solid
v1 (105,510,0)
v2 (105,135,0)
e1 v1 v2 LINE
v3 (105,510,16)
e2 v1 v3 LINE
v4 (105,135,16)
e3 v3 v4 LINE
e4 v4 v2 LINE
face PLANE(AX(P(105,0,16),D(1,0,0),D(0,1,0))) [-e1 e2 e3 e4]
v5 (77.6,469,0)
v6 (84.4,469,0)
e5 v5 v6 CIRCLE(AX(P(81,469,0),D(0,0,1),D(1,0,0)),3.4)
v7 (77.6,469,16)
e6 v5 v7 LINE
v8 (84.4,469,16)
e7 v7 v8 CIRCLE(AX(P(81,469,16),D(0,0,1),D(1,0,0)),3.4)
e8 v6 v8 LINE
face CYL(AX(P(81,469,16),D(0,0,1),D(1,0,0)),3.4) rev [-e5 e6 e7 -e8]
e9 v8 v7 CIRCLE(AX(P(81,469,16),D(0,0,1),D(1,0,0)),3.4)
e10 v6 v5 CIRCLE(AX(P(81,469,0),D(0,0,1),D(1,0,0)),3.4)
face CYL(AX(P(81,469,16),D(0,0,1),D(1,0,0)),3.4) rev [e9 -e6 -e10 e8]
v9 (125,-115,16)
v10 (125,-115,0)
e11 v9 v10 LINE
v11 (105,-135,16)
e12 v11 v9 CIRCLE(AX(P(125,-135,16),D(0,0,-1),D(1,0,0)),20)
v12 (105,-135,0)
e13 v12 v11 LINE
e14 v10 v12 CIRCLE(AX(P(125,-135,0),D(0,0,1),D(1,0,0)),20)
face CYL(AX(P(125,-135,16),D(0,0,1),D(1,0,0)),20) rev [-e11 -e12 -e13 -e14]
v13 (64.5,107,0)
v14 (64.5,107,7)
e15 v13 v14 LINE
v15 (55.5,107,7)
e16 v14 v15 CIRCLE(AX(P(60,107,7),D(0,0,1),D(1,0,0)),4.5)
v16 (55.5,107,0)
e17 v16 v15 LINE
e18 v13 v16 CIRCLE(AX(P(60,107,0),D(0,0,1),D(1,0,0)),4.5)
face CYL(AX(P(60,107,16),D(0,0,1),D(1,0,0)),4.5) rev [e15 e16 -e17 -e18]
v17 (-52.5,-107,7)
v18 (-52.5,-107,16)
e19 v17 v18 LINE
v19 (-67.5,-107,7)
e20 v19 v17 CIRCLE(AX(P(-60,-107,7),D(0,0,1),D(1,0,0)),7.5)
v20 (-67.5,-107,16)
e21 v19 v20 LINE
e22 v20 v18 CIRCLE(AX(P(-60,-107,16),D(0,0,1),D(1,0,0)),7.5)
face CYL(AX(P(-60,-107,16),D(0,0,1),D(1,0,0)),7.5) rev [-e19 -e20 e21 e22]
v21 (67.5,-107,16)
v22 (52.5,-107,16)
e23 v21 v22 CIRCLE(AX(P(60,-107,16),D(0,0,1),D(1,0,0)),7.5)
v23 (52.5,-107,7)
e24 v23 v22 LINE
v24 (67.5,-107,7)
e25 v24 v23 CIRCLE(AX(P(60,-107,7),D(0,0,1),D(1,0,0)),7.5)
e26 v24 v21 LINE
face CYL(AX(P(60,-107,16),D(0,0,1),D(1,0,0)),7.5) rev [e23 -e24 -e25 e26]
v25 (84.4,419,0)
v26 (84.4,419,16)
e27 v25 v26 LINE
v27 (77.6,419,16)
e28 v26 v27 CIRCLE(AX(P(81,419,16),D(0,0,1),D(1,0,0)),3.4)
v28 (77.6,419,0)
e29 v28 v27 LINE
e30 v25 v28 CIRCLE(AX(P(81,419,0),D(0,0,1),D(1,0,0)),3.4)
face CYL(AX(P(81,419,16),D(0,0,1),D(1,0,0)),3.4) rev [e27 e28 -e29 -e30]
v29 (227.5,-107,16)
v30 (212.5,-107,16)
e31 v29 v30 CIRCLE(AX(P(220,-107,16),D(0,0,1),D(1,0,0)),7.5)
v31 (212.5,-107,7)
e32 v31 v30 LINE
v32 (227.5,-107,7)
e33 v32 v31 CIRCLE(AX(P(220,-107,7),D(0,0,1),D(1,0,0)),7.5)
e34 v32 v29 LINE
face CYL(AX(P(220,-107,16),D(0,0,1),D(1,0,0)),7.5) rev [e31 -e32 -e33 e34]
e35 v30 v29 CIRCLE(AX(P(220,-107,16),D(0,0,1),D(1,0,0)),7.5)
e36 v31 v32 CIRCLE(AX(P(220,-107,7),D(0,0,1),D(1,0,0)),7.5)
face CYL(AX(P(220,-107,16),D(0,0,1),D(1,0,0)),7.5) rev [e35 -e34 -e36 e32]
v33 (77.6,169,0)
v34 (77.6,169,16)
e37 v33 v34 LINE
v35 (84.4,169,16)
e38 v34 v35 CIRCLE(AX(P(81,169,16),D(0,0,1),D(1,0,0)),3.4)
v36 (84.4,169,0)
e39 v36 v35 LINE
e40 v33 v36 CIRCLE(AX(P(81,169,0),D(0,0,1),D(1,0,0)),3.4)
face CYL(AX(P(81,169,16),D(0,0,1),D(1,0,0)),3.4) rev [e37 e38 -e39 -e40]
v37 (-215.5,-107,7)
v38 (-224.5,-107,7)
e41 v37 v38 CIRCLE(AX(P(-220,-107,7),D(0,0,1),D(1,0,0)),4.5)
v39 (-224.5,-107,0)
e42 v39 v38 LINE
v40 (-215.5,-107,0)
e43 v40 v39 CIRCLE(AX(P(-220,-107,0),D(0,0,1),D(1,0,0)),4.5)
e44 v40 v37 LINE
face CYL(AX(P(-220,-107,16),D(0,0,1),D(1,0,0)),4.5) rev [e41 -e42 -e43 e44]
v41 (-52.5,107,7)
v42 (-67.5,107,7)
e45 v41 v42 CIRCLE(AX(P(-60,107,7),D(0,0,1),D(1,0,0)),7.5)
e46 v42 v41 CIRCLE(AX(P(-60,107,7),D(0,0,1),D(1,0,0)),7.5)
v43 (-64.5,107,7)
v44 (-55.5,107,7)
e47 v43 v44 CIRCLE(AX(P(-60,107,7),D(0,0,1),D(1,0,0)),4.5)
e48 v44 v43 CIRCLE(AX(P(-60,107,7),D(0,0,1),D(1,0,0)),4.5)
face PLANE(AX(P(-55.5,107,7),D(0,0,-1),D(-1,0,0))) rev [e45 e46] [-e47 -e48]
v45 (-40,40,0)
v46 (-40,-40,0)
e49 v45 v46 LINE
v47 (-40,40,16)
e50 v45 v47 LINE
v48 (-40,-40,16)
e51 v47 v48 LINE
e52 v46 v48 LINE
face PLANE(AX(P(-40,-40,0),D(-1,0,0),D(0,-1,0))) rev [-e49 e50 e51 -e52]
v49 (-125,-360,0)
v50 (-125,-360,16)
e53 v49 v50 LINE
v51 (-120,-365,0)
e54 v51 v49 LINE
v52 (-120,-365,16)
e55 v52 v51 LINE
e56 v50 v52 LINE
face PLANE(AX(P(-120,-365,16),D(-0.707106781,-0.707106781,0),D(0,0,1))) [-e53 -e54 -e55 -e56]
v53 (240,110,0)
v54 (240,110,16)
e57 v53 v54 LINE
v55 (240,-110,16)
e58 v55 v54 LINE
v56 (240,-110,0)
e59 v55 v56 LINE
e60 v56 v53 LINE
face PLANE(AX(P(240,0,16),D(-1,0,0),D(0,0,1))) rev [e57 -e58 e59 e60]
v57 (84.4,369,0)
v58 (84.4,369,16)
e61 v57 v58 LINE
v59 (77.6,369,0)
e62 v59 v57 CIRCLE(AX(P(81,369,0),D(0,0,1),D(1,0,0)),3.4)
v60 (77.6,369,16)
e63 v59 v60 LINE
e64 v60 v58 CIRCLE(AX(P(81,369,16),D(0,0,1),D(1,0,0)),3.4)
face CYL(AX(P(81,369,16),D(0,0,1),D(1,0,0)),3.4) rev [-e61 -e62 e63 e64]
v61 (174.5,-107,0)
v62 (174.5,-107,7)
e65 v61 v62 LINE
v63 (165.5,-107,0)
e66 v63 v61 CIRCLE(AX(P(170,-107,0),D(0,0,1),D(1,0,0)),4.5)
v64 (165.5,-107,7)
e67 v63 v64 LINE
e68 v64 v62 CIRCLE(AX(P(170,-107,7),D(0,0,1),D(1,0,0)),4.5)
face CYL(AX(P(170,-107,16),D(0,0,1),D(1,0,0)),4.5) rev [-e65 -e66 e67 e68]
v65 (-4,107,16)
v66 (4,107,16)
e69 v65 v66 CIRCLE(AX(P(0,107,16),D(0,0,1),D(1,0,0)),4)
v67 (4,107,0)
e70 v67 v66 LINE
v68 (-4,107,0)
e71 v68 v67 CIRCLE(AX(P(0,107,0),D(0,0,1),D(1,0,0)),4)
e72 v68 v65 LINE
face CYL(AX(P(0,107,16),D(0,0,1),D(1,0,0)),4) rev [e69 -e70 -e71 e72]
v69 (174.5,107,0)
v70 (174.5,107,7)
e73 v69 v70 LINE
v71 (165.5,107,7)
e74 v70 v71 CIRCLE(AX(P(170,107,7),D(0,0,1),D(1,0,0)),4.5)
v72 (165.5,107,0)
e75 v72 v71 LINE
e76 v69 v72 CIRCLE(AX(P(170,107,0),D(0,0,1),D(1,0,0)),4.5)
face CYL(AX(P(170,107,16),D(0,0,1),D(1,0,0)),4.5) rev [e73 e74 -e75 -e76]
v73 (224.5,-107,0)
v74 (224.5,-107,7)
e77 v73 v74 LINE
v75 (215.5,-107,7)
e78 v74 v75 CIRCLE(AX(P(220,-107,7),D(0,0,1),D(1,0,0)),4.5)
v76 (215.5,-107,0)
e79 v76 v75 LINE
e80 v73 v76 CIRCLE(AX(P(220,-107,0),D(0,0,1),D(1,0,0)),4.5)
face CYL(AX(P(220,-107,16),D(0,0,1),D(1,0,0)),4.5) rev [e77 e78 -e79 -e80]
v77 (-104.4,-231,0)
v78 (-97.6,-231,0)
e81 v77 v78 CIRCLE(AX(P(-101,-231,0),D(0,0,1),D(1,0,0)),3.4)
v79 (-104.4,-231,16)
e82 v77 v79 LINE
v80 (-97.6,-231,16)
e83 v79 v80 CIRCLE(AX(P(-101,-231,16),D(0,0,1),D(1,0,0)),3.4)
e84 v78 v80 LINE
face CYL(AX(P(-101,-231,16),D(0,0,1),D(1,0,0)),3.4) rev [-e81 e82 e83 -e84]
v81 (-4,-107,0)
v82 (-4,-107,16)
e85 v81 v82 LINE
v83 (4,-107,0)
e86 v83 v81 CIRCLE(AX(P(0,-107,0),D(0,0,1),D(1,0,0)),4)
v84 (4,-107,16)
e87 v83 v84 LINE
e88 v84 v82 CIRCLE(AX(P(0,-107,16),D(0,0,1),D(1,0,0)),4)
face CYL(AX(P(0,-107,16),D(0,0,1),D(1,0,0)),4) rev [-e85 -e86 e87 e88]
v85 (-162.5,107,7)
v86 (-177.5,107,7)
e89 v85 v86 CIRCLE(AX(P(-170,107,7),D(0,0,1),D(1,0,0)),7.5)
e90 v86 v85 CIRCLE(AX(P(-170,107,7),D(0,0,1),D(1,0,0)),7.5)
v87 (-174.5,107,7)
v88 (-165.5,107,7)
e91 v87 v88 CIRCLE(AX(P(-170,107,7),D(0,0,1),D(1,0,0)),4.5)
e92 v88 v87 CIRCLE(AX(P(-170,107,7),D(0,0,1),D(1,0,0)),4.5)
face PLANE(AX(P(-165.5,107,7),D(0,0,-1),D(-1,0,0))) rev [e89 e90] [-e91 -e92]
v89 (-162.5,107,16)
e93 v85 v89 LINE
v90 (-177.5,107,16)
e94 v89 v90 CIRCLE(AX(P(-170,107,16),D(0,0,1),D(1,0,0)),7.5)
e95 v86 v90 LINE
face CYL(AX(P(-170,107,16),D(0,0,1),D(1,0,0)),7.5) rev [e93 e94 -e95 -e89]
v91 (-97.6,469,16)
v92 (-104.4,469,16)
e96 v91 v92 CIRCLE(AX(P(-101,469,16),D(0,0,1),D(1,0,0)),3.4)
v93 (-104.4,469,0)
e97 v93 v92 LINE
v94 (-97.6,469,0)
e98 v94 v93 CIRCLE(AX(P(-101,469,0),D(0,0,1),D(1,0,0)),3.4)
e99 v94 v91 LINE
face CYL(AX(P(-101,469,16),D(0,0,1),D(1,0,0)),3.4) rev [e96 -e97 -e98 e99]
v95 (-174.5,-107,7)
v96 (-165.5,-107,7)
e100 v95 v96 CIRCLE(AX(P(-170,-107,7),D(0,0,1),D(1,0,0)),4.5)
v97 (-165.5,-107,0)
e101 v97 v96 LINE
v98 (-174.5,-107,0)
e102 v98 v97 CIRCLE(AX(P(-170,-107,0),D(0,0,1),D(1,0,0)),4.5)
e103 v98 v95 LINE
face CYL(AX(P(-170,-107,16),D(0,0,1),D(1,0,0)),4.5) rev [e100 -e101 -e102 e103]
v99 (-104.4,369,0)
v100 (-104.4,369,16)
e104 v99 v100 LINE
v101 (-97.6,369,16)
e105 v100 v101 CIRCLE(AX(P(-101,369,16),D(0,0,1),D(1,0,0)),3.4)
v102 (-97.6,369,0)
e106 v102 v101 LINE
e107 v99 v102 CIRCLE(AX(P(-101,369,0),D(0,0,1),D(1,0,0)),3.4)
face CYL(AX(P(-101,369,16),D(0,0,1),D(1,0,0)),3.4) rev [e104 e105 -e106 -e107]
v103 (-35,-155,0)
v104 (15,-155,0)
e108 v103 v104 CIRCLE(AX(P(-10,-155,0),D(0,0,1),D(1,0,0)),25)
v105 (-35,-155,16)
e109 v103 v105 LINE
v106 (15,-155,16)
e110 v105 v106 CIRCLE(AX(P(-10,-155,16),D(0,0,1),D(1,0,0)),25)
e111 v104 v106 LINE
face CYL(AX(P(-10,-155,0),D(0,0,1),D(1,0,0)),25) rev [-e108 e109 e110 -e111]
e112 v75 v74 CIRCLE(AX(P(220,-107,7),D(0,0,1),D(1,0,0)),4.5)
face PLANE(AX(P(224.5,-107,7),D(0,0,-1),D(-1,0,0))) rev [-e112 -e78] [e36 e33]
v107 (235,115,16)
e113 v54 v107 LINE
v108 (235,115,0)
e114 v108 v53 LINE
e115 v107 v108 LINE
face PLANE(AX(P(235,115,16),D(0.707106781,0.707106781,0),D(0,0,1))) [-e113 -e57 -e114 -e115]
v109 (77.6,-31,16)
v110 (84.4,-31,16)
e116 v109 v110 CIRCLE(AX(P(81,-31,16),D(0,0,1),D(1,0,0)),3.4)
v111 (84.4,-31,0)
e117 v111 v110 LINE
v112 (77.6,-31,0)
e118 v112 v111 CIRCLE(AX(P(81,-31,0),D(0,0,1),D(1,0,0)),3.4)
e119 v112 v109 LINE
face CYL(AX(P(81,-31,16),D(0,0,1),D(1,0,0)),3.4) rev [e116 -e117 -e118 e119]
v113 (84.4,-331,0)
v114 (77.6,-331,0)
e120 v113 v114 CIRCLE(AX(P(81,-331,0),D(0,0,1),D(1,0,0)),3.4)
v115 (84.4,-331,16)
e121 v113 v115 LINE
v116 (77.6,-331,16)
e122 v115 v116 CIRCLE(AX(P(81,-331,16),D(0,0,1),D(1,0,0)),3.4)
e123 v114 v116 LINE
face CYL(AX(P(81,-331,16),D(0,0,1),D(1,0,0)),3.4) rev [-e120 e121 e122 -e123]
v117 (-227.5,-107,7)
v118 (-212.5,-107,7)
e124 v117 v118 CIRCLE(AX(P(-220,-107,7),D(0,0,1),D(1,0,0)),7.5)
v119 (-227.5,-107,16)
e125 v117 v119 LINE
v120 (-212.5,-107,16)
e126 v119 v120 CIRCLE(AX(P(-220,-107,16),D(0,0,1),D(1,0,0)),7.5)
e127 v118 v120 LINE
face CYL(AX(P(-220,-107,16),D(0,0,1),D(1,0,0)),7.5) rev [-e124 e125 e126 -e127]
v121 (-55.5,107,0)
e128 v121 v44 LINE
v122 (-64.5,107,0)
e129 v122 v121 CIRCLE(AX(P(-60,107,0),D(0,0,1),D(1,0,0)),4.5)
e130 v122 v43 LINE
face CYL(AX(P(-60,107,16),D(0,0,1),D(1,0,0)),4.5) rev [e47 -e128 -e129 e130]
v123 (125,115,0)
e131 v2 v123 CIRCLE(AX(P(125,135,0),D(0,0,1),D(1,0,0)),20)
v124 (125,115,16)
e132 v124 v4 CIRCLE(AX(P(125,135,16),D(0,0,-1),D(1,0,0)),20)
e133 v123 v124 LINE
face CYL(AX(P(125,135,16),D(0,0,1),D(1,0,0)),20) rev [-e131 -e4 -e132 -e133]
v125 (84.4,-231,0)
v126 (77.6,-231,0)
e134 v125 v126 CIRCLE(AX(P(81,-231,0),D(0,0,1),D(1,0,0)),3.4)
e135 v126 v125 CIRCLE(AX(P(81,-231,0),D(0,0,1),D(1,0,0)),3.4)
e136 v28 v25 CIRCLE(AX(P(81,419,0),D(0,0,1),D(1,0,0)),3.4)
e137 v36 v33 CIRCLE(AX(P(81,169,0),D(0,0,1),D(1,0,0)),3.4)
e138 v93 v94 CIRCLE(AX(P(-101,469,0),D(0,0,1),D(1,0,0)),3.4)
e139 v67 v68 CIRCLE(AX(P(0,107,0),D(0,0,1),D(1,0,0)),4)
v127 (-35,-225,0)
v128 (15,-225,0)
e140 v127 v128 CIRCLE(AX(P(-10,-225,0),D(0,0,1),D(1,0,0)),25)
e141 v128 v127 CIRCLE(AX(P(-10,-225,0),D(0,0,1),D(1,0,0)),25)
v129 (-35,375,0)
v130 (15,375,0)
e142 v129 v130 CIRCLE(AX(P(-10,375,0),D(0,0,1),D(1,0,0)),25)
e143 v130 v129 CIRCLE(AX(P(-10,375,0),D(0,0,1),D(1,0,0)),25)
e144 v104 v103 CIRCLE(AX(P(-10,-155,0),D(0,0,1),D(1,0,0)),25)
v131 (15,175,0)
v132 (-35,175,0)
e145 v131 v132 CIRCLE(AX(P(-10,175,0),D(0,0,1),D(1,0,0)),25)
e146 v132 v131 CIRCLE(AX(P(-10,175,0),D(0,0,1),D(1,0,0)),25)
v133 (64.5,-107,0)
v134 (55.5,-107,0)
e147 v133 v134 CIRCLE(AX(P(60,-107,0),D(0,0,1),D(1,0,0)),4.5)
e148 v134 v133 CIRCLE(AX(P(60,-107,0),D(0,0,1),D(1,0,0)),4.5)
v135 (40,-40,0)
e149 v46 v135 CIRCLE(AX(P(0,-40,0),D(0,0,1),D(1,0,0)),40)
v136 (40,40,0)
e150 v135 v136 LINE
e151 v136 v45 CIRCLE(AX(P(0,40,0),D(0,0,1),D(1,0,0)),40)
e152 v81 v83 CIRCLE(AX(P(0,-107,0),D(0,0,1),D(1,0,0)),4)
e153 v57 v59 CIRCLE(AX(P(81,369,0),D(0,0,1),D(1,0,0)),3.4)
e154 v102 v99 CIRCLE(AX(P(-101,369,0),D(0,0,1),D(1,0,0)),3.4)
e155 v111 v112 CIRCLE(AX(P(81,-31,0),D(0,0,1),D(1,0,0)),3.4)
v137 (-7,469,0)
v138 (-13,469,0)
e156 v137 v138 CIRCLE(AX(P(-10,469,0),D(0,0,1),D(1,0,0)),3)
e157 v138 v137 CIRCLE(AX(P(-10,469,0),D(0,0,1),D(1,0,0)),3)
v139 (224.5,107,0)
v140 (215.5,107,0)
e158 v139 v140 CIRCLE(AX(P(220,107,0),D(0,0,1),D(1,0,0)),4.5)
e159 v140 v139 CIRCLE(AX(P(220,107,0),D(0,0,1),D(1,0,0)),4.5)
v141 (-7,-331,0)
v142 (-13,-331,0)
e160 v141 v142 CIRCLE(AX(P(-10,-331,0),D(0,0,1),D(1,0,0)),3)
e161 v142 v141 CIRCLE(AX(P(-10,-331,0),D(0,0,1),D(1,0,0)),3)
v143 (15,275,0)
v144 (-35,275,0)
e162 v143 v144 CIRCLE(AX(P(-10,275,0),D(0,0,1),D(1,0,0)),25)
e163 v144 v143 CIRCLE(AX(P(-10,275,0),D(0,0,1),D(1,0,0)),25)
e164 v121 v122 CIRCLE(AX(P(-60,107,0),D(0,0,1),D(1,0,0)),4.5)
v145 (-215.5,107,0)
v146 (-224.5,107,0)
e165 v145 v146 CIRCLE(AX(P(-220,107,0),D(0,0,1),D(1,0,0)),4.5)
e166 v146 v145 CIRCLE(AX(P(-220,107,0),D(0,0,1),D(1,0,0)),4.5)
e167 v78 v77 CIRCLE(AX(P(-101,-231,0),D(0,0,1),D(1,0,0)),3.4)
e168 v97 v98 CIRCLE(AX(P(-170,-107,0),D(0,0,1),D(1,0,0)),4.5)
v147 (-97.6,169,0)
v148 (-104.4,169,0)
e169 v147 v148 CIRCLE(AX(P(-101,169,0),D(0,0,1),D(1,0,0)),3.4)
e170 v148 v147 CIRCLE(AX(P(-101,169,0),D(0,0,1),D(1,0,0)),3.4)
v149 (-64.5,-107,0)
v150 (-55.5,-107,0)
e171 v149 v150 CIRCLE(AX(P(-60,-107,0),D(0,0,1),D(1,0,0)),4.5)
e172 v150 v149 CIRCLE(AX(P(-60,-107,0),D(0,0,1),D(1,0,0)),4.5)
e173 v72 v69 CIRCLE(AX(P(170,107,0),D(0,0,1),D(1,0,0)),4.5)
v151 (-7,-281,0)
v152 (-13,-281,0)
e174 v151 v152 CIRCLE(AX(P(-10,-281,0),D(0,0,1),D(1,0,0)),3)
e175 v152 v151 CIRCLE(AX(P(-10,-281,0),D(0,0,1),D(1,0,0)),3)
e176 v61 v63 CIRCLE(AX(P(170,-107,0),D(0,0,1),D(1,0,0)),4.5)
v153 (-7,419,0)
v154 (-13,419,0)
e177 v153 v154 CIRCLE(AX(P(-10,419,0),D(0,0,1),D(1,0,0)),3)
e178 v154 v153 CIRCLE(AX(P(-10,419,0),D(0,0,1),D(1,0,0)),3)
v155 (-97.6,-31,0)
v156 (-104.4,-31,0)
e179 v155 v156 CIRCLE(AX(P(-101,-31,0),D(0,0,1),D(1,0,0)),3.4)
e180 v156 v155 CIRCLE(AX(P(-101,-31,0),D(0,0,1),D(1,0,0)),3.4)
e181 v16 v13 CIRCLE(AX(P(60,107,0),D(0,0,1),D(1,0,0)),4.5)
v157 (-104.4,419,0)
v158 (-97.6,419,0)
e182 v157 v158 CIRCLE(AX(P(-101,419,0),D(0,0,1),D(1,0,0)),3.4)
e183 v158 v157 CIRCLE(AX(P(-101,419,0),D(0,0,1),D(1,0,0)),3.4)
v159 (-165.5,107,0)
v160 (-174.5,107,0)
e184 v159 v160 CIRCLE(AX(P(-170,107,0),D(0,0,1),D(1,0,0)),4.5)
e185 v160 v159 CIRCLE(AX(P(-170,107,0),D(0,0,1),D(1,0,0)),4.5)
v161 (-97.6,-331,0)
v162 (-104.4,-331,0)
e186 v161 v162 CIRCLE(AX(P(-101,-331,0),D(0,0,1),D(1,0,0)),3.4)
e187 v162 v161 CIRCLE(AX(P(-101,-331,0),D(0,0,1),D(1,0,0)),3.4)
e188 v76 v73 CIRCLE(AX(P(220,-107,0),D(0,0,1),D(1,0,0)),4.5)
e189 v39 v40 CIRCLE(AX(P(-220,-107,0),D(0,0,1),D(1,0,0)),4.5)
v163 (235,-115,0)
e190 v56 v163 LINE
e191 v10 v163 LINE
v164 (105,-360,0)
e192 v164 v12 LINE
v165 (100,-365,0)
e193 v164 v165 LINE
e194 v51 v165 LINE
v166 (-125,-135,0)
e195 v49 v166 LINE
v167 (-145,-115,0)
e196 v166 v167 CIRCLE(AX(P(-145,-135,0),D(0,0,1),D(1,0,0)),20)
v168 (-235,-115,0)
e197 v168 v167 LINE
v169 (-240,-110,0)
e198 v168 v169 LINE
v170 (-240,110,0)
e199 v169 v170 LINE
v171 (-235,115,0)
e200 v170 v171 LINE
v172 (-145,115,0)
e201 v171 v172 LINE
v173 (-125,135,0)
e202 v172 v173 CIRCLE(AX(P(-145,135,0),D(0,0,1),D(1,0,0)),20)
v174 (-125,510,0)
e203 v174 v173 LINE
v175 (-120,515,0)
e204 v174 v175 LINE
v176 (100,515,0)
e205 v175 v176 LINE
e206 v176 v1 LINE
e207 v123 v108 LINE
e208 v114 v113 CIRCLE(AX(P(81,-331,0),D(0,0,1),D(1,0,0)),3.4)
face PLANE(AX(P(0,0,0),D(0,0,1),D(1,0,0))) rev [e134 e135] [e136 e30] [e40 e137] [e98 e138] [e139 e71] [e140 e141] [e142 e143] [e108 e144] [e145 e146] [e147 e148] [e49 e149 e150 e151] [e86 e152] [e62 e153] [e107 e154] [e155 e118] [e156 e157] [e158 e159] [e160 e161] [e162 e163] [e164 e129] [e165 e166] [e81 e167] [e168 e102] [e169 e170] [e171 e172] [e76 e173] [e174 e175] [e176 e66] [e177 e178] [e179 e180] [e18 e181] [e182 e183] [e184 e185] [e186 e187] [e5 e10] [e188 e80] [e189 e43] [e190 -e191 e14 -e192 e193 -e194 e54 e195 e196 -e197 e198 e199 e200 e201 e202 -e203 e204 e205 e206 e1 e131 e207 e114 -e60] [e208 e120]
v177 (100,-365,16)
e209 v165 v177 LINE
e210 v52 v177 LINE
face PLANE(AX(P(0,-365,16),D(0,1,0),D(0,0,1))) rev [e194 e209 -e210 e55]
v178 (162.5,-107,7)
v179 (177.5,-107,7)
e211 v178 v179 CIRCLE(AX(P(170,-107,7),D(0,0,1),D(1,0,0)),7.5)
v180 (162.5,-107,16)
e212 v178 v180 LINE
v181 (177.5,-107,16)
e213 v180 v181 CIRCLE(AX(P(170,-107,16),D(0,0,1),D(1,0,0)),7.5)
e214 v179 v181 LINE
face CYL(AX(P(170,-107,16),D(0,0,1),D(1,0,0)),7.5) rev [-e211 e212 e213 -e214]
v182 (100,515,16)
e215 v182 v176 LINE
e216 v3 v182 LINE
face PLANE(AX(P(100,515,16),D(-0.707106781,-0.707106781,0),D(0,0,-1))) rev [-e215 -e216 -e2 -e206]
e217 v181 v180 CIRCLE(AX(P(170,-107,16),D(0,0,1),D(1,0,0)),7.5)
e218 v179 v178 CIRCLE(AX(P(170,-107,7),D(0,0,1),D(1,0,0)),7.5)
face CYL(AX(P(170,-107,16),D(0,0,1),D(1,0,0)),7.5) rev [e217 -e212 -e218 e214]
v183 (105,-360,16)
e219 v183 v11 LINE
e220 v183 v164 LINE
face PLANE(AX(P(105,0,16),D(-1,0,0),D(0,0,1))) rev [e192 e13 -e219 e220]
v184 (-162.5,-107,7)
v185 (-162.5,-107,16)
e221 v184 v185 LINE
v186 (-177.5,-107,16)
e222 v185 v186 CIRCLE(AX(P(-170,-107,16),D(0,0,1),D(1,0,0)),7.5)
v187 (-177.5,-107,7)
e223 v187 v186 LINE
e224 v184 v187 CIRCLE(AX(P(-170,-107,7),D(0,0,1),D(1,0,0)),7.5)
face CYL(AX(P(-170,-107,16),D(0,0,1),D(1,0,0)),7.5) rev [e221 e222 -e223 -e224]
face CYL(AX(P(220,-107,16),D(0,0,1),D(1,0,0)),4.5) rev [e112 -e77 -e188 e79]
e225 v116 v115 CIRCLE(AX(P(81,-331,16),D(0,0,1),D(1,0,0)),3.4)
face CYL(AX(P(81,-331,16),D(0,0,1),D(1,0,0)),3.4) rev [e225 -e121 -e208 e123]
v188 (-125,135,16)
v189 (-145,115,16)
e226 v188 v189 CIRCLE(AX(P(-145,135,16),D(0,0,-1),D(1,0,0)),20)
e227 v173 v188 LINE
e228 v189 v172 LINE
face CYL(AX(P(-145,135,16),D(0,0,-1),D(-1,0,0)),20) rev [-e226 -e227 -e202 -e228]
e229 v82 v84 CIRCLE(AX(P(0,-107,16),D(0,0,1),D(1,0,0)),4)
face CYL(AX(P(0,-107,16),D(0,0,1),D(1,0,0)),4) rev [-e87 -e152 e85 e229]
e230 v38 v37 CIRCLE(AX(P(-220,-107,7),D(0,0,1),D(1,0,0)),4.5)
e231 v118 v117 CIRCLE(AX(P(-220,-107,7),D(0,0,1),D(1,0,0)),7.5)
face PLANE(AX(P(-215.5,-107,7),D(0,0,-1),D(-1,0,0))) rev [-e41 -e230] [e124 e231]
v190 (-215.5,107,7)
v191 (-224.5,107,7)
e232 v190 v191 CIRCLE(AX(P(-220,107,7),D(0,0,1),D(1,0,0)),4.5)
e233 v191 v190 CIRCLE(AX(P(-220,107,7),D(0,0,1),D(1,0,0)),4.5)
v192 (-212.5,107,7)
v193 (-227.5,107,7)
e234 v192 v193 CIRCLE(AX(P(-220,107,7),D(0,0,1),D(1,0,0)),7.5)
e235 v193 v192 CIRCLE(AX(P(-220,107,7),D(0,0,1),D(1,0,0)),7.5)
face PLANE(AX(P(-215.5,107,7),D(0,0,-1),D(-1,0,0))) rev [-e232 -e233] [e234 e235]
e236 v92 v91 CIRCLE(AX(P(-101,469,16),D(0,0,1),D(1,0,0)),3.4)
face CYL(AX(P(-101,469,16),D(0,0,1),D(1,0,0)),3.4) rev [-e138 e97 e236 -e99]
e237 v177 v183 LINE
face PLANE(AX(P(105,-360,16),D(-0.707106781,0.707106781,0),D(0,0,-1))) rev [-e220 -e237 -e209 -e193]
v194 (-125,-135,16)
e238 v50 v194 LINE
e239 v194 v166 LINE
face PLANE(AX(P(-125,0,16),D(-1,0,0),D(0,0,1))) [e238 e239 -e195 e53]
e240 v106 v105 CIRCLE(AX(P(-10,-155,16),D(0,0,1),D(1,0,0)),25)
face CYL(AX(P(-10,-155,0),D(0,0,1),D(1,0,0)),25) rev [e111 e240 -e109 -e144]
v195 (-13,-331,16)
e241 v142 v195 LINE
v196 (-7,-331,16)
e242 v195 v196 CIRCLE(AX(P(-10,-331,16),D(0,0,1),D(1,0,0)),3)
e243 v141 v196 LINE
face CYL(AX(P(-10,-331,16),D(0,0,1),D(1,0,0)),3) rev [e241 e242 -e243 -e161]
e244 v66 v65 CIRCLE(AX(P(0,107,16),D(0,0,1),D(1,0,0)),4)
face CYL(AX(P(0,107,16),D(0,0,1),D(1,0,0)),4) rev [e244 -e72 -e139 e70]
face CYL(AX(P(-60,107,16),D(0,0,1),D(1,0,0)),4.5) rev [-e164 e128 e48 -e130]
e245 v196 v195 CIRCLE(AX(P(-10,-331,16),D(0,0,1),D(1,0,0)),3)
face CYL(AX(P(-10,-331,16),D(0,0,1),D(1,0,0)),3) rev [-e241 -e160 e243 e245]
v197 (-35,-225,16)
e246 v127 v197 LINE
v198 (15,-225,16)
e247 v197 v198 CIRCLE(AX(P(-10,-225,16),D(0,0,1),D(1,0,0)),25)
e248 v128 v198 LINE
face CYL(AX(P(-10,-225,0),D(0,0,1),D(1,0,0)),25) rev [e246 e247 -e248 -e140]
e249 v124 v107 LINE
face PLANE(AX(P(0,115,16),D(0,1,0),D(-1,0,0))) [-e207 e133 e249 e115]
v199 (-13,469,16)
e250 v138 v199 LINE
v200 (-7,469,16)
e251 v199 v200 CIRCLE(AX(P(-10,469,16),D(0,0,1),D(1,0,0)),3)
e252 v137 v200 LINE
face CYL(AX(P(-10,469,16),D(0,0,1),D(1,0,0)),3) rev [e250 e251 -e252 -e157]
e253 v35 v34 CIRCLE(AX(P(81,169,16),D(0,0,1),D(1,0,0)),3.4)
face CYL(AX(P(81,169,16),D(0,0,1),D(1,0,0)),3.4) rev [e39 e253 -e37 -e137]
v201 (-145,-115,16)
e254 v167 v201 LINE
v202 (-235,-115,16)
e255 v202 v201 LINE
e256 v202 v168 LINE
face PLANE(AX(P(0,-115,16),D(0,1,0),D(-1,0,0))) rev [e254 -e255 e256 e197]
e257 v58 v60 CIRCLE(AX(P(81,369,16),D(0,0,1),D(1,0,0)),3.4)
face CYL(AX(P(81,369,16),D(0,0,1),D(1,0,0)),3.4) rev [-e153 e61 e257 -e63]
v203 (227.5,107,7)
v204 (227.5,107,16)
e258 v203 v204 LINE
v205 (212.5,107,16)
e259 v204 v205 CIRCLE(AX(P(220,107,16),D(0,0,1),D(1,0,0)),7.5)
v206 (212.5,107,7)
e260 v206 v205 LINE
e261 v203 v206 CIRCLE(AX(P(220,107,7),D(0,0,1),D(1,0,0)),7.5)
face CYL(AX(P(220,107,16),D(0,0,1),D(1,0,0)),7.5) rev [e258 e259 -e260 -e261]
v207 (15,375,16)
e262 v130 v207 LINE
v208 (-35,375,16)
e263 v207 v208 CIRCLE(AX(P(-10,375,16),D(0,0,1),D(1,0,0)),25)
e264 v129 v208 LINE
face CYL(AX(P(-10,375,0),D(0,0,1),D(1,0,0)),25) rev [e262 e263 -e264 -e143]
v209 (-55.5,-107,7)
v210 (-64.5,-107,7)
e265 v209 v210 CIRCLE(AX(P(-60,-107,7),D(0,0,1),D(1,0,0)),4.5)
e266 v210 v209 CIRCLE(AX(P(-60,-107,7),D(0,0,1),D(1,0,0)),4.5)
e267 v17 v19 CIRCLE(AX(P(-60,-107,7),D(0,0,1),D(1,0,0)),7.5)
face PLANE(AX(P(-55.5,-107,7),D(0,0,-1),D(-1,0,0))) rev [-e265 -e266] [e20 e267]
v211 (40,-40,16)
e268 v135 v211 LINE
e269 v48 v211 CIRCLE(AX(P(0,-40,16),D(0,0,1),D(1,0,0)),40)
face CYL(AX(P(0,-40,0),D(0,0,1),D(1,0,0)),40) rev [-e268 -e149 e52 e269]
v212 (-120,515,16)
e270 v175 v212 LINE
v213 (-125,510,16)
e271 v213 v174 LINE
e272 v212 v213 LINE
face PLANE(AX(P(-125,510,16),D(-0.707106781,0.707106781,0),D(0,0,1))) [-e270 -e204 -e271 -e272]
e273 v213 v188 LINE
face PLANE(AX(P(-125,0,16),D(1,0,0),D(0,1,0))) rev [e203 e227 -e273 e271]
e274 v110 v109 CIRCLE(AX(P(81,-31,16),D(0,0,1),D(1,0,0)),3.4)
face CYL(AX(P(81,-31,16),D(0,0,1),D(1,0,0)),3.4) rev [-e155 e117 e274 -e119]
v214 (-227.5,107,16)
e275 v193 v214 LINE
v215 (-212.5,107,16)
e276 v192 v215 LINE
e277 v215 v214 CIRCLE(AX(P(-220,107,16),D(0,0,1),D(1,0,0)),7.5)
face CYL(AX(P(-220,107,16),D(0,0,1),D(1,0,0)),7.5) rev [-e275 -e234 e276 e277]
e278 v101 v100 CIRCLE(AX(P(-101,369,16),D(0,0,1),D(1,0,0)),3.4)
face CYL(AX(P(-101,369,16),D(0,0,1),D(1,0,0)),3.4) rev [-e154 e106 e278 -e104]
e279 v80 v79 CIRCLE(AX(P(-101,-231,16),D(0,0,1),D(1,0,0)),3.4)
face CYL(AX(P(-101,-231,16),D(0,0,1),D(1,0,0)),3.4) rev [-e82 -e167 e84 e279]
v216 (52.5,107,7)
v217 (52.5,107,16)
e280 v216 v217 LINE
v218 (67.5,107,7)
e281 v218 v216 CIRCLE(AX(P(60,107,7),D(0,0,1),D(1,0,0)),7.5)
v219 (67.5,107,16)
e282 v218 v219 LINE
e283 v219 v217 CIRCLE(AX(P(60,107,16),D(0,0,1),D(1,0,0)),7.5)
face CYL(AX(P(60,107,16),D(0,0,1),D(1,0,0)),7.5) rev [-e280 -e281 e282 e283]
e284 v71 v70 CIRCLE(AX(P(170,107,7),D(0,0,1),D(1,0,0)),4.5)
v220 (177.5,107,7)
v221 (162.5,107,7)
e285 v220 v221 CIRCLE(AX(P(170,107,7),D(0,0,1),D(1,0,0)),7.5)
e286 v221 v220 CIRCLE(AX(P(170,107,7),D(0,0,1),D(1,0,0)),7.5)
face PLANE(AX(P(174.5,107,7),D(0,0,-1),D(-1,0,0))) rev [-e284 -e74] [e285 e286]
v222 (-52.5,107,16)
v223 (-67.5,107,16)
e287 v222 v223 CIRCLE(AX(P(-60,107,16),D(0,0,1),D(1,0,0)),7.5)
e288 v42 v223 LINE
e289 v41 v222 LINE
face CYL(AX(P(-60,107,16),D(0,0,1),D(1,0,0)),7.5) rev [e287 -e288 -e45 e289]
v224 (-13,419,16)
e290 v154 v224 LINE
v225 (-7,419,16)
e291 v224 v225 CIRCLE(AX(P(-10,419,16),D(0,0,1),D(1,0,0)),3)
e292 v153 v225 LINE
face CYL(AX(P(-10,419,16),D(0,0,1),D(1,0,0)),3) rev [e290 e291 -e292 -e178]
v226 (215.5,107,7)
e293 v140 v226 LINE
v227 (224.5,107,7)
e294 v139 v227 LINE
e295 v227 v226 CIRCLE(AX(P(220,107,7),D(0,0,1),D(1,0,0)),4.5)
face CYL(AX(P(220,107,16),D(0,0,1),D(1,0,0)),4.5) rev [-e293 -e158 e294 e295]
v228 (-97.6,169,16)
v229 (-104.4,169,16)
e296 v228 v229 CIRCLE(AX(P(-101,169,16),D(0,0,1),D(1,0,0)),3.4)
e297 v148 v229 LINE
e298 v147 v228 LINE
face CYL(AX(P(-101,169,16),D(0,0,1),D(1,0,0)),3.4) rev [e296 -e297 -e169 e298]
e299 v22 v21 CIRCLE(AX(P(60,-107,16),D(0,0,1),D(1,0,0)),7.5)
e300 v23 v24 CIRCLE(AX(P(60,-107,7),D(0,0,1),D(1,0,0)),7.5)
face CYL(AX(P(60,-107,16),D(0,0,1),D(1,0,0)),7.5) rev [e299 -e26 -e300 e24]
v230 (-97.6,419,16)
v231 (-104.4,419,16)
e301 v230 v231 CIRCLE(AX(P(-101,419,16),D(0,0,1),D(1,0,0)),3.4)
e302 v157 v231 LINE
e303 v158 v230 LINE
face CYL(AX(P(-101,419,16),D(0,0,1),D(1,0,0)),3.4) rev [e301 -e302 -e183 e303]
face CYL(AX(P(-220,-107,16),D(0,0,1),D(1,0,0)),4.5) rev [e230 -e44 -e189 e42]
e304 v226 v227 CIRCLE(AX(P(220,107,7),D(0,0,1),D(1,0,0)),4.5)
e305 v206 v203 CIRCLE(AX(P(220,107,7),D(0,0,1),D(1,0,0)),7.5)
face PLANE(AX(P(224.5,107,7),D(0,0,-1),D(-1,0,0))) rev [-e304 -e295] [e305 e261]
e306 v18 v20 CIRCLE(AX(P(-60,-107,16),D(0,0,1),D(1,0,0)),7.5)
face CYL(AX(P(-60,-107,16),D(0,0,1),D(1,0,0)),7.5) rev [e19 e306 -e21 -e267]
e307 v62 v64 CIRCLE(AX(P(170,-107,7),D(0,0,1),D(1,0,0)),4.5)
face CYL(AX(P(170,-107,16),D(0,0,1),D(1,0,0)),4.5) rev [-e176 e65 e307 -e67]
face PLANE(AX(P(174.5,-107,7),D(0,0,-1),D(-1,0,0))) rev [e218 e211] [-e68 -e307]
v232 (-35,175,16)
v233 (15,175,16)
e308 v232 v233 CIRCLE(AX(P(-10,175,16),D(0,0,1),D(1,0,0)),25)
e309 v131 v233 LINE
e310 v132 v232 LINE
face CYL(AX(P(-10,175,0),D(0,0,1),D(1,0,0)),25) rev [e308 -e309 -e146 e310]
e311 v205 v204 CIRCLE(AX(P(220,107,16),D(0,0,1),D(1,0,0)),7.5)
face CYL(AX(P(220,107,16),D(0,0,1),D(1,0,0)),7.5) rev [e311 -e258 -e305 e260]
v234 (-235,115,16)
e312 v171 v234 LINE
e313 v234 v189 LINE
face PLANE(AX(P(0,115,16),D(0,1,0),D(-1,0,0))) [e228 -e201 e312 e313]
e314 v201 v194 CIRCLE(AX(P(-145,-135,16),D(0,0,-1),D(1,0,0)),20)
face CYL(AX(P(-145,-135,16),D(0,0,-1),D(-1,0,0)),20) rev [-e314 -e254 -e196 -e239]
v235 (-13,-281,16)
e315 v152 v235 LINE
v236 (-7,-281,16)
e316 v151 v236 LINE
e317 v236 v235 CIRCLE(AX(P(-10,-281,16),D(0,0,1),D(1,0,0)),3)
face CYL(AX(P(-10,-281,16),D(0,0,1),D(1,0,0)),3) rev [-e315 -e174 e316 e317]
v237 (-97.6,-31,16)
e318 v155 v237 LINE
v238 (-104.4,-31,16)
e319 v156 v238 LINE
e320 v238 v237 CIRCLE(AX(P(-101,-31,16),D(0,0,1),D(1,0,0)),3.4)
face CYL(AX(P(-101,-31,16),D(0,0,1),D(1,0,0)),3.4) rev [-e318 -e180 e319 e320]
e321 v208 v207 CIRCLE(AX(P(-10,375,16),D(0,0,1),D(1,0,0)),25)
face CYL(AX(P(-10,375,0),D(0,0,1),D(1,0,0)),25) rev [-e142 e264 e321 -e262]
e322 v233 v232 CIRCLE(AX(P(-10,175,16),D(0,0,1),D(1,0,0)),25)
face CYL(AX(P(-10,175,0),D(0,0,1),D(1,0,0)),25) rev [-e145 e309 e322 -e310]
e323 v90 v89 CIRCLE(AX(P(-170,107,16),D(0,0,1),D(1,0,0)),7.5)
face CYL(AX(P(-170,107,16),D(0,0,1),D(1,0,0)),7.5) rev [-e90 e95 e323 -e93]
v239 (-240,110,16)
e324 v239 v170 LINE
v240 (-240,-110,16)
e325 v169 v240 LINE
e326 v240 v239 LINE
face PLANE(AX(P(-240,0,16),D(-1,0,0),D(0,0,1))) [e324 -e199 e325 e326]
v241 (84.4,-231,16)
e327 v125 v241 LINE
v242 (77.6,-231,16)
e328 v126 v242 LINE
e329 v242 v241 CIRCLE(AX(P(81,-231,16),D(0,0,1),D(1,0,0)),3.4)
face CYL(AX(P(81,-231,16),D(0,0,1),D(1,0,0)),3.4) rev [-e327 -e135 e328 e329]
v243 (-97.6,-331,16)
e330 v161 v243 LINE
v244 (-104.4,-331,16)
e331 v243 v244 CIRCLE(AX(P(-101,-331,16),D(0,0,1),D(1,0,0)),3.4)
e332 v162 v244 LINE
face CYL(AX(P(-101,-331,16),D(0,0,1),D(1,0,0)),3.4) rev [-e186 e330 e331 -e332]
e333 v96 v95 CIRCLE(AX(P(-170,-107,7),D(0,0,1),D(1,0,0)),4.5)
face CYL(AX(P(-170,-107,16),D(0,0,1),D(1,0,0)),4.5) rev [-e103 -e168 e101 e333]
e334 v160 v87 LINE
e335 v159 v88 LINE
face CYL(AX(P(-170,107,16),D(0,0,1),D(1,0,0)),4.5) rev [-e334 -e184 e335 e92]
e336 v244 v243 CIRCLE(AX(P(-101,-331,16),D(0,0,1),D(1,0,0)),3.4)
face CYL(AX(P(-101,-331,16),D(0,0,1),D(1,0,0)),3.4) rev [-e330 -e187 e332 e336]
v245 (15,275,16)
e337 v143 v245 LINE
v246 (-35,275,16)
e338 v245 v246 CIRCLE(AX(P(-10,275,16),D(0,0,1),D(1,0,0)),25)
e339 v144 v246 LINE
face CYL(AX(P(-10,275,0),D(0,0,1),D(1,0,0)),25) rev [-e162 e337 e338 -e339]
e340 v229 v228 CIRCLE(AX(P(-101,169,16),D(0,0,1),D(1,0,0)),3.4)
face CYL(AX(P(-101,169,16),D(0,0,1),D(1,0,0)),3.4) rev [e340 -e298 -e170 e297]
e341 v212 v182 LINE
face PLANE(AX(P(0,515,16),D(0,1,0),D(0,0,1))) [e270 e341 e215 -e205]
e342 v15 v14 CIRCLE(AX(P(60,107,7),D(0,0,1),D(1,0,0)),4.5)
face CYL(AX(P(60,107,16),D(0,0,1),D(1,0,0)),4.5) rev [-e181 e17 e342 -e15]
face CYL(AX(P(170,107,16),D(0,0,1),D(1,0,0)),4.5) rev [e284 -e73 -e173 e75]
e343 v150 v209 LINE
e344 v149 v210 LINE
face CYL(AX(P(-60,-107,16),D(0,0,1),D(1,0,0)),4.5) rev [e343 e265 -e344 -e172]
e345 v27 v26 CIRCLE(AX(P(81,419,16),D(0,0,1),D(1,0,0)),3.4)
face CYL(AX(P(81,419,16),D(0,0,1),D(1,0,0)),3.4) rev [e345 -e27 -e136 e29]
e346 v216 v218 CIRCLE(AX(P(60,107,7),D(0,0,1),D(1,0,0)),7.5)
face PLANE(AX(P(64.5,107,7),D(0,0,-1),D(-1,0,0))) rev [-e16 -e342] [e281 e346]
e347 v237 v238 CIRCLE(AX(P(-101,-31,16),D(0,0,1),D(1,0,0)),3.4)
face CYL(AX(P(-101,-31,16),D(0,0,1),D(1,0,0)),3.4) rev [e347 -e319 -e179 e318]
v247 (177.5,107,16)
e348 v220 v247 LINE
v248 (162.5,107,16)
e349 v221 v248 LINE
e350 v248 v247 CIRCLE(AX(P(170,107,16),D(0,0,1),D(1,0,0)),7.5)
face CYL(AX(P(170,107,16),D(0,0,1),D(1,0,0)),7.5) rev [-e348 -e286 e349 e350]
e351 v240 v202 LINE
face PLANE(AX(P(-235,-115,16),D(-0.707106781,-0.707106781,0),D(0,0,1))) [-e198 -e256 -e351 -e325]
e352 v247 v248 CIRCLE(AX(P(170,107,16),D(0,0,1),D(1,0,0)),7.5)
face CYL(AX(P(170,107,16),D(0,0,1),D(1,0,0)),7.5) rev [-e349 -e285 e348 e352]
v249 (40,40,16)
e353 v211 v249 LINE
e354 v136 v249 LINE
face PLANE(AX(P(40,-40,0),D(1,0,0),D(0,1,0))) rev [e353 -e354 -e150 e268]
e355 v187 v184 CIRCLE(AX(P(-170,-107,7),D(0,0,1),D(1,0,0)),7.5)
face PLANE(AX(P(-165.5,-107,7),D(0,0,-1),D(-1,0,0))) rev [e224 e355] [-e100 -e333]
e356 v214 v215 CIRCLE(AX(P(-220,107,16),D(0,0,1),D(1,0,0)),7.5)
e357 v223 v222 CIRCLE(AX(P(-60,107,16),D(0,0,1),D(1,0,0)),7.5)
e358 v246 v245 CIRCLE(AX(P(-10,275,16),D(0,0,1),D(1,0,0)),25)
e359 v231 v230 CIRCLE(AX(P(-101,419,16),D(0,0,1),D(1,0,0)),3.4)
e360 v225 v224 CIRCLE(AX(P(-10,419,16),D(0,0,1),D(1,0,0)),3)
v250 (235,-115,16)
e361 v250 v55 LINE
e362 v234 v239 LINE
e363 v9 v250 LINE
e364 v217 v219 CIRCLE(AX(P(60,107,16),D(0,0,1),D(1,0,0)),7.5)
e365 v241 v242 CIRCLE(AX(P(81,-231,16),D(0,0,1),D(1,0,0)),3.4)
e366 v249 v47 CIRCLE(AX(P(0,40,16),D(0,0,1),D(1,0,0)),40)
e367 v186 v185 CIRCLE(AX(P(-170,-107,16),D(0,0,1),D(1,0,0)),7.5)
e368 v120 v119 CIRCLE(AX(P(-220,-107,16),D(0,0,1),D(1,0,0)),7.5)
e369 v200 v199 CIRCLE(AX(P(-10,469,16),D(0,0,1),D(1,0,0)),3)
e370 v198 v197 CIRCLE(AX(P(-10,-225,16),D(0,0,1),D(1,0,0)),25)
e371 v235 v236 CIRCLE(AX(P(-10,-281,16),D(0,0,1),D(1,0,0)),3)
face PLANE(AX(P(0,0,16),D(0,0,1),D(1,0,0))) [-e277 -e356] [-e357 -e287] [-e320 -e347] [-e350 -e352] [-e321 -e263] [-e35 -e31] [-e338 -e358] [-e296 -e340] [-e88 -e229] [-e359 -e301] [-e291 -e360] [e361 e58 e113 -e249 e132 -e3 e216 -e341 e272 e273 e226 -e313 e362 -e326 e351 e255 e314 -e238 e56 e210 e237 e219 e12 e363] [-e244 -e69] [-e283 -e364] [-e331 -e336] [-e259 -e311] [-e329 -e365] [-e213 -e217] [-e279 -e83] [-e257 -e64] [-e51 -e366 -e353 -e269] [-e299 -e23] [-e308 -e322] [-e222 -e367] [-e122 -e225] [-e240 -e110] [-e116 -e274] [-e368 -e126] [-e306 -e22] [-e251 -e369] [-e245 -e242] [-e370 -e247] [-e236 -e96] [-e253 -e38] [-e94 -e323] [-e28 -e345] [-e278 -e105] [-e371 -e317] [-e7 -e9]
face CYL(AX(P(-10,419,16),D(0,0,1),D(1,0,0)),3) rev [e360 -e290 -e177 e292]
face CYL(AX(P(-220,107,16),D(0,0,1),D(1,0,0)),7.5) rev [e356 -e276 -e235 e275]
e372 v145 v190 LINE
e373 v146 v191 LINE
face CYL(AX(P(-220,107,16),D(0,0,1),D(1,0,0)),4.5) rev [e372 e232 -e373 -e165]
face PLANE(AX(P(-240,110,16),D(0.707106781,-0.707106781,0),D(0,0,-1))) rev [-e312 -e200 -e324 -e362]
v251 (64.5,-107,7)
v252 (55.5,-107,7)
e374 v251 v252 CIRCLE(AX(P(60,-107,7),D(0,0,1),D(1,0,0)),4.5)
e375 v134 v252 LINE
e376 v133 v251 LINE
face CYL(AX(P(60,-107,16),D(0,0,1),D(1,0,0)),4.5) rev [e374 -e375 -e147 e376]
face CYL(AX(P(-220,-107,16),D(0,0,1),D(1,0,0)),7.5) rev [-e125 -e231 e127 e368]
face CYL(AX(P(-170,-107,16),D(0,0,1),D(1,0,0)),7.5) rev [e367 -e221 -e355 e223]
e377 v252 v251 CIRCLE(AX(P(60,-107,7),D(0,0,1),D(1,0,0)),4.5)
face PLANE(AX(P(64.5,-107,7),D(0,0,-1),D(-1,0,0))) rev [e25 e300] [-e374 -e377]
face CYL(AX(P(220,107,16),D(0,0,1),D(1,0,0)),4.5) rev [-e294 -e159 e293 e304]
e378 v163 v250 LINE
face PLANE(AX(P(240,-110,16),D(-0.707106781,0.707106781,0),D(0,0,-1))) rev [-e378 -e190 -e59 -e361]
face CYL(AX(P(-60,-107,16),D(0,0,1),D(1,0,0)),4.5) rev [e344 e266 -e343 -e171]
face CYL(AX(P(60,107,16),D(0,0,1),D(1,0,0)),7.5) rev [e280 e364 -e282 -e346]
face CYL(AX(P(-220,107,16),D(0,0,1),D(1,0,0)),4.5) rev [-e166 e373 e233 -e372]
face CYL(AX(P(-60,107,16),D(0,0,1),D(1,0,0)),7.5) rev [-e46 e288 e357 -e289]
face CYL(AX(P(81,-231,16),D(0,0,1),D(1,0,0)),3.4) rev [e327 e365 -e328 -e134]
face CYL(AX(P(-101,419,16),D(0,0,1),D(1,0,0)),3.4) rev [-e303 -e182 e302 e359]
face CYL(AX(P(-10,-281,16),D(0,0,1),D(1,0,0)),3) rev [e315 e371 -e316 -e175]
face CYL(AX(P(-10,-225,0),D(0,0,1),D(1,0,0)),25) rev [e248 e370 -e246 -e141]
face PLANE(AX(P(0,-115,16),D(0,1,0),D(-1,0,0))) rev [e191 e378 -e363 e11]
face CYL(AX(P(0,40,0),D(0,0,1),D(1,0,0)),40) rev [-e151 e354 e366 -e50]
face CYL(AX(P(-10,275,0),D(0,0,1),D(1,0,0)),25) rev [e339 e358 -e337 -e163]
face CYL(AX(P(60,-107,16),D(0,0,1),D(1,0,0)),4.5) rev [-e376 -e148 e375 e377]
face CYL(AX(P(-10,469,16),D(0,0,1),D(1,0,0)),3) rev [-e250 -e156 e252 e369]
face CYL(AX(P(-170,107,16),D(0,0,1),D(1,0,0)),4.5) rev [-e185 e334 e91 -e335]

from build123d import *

# Parameters (mm, degrees)
SKETCH_1_W                = 230
SKETCH_1_H                = 400
SKETCH_1_W_2              = 480
SKETCH_1_H_2              = 230
SKETCH_1_H_3              = 250
EXTRUDE_1_DEPTH           = 16
FILLET_1_R                = 20
HOLE_WIZARD_1_D           = 9
HOLE_WIZARD_1_CBORE_D     = 15
HOLE_WIZARD_1_CBORE_DEPTH = 9
MM_1_D                    = 8
HOLE_WIZARD_M8_1_D        = 6.8
HOLE_WIZARD_M8_1_DEPTH    = 22.25
HOLE_WIZARD_M8_1_TIP      = 2.042926105
CHAMFER_1_SIZE            = 5
SKETCH_8_R                = 25
CUT_EXTRUDE_1_DEPTH       = 569.402146372
MM_4_D                    = 6


with BuildPart() as part:
    # 草图1 → 凸台-拉伸1 (new body)
    with BuildSketch(Plane.XY):
        with Locations((-10, 315)):
            Rectangle(SKETCH_1_W, SKETCH_1_H)
        Rectangle(SKETCH_1_W_2, SKETCH_1_H_2)
        with Locations((-10, -240)):
            Rectangle(SKETCH_1_W, SKETCH_1_H_3)
    extrude(amount=EXTRUDE_1_DEPTH)

    # 圆角1
    fillet_1_edges = [part.edges().sort_by_distance(p)[0] for p in [
        (105, 115, 8),
        (105, -115, 8),
        (-125, -115, 8),
        (-125, 115, 8),
    ]]
    fillet(fillet_1_edges, radius=FILLET_1_R)

    # 打孔尺寸(%根据)内六角圆柱头螺钉的类型1 (through all)
    with Locations(Plane.XY.offset(16)):
        with Locations((60, -107), (220, 107), (-220, -107), (-220, 107), (220, -107), (-170, 107), (-170, -107), (170, 107), (170, -107), (-60, 107), (-60, -107), (60, 107)):
            CounterBoreHole(HOLE_WIZARD_1_D / 2, HOLE_WIZARD_1_CBORE_D / 2, HOLE_WIZARD_1_CBORE_DEPTH)

    # 大小mm 暗销孔1 (through all)
    with Locations(Plane.XY.offset(16)):
        with Locations((0, 107), (0, -107)):
            Hole(MM_1_D / 2)

    # M8 螺纹孔1
    with Locations(Plane.XY.offset(16)):
        with Locations((81, 469), (-101, 469), (-101, 169), (-101, 369), (-101, 419), (-101, -31), (-101, -231), (-101, -331), (81, -331), (81, -231), (81, -31), (81, 419), (81, 369), (81, 169)):
            Hole(HOLE_WIZARD_M8_1_D / 2, depth=HOLE_WIZARD_M8_1_DEPTH)
            with Locations((0, 0, -(HOLE_WIZARD_M8_1_DEPTH + HOLE_WIZARD_M8_1_TIP / 2))):  # 118° drill point
                Cone(0, HOLE_WIZARD_M8_1_D / 2, HOLE_WIZARD_M8_1_TIP, mode=Mode.SUBTRACT)

    # 倒角1
    chamfer_1_edges = [part.edges().sort_by_distance(p)[0] for p in [
        (240, 115, 8),
        (240, -115, 8),
        (105, -365, 8),
        (-125, -365, 8),
        (-240, -115, 8),
        (-240, 115, 8),
        (-125, 515, 8),
        (105, 515, 8),
    ]]
    chamfer(chamfer_1_edges, length=CHAMFER_1_SIZE)

    # 草图8 → 切除-拉伸1 (cut, through all)
    with BuildSketch(Plane.XY.offset(16)):
        with Locations((-10, 375)):
            Circle(SKETCH_8_R)
        with Locations((-10, -155)):
            Circle(SKETCH_8_R)
        with Locations((-10, -225)):
            Circle(SKETCH_8_R)
        with Locations((-10, 275)):
            Circle(SKETCH_8_R)
        with Locations((-10, 175)):
            Circle(SKETCH_8_R)
        with BuildLine():
            Line((-40, -40), (-40, 40))
            ThreePointArc((-40, 40), (0, 80), (40, 40))
            Line((40, 40), (40, -40))
            ThreePointArc((40, -40), (0, -80), (-40, -40))
        make_face()
    extrude(amount=-CUT_EXTRUDE_1_DEPTH, mode=Mode.SUBTRACT)

    # 大小mm 暗销孔4 (through all)
    with Locations(Plane.XY.offset(16)):
        with Locations((-10, 419), (-10, -331), (-10, -281), (-10, 469)):
            Hole(MM_4_D / 2)


solid = part.part
